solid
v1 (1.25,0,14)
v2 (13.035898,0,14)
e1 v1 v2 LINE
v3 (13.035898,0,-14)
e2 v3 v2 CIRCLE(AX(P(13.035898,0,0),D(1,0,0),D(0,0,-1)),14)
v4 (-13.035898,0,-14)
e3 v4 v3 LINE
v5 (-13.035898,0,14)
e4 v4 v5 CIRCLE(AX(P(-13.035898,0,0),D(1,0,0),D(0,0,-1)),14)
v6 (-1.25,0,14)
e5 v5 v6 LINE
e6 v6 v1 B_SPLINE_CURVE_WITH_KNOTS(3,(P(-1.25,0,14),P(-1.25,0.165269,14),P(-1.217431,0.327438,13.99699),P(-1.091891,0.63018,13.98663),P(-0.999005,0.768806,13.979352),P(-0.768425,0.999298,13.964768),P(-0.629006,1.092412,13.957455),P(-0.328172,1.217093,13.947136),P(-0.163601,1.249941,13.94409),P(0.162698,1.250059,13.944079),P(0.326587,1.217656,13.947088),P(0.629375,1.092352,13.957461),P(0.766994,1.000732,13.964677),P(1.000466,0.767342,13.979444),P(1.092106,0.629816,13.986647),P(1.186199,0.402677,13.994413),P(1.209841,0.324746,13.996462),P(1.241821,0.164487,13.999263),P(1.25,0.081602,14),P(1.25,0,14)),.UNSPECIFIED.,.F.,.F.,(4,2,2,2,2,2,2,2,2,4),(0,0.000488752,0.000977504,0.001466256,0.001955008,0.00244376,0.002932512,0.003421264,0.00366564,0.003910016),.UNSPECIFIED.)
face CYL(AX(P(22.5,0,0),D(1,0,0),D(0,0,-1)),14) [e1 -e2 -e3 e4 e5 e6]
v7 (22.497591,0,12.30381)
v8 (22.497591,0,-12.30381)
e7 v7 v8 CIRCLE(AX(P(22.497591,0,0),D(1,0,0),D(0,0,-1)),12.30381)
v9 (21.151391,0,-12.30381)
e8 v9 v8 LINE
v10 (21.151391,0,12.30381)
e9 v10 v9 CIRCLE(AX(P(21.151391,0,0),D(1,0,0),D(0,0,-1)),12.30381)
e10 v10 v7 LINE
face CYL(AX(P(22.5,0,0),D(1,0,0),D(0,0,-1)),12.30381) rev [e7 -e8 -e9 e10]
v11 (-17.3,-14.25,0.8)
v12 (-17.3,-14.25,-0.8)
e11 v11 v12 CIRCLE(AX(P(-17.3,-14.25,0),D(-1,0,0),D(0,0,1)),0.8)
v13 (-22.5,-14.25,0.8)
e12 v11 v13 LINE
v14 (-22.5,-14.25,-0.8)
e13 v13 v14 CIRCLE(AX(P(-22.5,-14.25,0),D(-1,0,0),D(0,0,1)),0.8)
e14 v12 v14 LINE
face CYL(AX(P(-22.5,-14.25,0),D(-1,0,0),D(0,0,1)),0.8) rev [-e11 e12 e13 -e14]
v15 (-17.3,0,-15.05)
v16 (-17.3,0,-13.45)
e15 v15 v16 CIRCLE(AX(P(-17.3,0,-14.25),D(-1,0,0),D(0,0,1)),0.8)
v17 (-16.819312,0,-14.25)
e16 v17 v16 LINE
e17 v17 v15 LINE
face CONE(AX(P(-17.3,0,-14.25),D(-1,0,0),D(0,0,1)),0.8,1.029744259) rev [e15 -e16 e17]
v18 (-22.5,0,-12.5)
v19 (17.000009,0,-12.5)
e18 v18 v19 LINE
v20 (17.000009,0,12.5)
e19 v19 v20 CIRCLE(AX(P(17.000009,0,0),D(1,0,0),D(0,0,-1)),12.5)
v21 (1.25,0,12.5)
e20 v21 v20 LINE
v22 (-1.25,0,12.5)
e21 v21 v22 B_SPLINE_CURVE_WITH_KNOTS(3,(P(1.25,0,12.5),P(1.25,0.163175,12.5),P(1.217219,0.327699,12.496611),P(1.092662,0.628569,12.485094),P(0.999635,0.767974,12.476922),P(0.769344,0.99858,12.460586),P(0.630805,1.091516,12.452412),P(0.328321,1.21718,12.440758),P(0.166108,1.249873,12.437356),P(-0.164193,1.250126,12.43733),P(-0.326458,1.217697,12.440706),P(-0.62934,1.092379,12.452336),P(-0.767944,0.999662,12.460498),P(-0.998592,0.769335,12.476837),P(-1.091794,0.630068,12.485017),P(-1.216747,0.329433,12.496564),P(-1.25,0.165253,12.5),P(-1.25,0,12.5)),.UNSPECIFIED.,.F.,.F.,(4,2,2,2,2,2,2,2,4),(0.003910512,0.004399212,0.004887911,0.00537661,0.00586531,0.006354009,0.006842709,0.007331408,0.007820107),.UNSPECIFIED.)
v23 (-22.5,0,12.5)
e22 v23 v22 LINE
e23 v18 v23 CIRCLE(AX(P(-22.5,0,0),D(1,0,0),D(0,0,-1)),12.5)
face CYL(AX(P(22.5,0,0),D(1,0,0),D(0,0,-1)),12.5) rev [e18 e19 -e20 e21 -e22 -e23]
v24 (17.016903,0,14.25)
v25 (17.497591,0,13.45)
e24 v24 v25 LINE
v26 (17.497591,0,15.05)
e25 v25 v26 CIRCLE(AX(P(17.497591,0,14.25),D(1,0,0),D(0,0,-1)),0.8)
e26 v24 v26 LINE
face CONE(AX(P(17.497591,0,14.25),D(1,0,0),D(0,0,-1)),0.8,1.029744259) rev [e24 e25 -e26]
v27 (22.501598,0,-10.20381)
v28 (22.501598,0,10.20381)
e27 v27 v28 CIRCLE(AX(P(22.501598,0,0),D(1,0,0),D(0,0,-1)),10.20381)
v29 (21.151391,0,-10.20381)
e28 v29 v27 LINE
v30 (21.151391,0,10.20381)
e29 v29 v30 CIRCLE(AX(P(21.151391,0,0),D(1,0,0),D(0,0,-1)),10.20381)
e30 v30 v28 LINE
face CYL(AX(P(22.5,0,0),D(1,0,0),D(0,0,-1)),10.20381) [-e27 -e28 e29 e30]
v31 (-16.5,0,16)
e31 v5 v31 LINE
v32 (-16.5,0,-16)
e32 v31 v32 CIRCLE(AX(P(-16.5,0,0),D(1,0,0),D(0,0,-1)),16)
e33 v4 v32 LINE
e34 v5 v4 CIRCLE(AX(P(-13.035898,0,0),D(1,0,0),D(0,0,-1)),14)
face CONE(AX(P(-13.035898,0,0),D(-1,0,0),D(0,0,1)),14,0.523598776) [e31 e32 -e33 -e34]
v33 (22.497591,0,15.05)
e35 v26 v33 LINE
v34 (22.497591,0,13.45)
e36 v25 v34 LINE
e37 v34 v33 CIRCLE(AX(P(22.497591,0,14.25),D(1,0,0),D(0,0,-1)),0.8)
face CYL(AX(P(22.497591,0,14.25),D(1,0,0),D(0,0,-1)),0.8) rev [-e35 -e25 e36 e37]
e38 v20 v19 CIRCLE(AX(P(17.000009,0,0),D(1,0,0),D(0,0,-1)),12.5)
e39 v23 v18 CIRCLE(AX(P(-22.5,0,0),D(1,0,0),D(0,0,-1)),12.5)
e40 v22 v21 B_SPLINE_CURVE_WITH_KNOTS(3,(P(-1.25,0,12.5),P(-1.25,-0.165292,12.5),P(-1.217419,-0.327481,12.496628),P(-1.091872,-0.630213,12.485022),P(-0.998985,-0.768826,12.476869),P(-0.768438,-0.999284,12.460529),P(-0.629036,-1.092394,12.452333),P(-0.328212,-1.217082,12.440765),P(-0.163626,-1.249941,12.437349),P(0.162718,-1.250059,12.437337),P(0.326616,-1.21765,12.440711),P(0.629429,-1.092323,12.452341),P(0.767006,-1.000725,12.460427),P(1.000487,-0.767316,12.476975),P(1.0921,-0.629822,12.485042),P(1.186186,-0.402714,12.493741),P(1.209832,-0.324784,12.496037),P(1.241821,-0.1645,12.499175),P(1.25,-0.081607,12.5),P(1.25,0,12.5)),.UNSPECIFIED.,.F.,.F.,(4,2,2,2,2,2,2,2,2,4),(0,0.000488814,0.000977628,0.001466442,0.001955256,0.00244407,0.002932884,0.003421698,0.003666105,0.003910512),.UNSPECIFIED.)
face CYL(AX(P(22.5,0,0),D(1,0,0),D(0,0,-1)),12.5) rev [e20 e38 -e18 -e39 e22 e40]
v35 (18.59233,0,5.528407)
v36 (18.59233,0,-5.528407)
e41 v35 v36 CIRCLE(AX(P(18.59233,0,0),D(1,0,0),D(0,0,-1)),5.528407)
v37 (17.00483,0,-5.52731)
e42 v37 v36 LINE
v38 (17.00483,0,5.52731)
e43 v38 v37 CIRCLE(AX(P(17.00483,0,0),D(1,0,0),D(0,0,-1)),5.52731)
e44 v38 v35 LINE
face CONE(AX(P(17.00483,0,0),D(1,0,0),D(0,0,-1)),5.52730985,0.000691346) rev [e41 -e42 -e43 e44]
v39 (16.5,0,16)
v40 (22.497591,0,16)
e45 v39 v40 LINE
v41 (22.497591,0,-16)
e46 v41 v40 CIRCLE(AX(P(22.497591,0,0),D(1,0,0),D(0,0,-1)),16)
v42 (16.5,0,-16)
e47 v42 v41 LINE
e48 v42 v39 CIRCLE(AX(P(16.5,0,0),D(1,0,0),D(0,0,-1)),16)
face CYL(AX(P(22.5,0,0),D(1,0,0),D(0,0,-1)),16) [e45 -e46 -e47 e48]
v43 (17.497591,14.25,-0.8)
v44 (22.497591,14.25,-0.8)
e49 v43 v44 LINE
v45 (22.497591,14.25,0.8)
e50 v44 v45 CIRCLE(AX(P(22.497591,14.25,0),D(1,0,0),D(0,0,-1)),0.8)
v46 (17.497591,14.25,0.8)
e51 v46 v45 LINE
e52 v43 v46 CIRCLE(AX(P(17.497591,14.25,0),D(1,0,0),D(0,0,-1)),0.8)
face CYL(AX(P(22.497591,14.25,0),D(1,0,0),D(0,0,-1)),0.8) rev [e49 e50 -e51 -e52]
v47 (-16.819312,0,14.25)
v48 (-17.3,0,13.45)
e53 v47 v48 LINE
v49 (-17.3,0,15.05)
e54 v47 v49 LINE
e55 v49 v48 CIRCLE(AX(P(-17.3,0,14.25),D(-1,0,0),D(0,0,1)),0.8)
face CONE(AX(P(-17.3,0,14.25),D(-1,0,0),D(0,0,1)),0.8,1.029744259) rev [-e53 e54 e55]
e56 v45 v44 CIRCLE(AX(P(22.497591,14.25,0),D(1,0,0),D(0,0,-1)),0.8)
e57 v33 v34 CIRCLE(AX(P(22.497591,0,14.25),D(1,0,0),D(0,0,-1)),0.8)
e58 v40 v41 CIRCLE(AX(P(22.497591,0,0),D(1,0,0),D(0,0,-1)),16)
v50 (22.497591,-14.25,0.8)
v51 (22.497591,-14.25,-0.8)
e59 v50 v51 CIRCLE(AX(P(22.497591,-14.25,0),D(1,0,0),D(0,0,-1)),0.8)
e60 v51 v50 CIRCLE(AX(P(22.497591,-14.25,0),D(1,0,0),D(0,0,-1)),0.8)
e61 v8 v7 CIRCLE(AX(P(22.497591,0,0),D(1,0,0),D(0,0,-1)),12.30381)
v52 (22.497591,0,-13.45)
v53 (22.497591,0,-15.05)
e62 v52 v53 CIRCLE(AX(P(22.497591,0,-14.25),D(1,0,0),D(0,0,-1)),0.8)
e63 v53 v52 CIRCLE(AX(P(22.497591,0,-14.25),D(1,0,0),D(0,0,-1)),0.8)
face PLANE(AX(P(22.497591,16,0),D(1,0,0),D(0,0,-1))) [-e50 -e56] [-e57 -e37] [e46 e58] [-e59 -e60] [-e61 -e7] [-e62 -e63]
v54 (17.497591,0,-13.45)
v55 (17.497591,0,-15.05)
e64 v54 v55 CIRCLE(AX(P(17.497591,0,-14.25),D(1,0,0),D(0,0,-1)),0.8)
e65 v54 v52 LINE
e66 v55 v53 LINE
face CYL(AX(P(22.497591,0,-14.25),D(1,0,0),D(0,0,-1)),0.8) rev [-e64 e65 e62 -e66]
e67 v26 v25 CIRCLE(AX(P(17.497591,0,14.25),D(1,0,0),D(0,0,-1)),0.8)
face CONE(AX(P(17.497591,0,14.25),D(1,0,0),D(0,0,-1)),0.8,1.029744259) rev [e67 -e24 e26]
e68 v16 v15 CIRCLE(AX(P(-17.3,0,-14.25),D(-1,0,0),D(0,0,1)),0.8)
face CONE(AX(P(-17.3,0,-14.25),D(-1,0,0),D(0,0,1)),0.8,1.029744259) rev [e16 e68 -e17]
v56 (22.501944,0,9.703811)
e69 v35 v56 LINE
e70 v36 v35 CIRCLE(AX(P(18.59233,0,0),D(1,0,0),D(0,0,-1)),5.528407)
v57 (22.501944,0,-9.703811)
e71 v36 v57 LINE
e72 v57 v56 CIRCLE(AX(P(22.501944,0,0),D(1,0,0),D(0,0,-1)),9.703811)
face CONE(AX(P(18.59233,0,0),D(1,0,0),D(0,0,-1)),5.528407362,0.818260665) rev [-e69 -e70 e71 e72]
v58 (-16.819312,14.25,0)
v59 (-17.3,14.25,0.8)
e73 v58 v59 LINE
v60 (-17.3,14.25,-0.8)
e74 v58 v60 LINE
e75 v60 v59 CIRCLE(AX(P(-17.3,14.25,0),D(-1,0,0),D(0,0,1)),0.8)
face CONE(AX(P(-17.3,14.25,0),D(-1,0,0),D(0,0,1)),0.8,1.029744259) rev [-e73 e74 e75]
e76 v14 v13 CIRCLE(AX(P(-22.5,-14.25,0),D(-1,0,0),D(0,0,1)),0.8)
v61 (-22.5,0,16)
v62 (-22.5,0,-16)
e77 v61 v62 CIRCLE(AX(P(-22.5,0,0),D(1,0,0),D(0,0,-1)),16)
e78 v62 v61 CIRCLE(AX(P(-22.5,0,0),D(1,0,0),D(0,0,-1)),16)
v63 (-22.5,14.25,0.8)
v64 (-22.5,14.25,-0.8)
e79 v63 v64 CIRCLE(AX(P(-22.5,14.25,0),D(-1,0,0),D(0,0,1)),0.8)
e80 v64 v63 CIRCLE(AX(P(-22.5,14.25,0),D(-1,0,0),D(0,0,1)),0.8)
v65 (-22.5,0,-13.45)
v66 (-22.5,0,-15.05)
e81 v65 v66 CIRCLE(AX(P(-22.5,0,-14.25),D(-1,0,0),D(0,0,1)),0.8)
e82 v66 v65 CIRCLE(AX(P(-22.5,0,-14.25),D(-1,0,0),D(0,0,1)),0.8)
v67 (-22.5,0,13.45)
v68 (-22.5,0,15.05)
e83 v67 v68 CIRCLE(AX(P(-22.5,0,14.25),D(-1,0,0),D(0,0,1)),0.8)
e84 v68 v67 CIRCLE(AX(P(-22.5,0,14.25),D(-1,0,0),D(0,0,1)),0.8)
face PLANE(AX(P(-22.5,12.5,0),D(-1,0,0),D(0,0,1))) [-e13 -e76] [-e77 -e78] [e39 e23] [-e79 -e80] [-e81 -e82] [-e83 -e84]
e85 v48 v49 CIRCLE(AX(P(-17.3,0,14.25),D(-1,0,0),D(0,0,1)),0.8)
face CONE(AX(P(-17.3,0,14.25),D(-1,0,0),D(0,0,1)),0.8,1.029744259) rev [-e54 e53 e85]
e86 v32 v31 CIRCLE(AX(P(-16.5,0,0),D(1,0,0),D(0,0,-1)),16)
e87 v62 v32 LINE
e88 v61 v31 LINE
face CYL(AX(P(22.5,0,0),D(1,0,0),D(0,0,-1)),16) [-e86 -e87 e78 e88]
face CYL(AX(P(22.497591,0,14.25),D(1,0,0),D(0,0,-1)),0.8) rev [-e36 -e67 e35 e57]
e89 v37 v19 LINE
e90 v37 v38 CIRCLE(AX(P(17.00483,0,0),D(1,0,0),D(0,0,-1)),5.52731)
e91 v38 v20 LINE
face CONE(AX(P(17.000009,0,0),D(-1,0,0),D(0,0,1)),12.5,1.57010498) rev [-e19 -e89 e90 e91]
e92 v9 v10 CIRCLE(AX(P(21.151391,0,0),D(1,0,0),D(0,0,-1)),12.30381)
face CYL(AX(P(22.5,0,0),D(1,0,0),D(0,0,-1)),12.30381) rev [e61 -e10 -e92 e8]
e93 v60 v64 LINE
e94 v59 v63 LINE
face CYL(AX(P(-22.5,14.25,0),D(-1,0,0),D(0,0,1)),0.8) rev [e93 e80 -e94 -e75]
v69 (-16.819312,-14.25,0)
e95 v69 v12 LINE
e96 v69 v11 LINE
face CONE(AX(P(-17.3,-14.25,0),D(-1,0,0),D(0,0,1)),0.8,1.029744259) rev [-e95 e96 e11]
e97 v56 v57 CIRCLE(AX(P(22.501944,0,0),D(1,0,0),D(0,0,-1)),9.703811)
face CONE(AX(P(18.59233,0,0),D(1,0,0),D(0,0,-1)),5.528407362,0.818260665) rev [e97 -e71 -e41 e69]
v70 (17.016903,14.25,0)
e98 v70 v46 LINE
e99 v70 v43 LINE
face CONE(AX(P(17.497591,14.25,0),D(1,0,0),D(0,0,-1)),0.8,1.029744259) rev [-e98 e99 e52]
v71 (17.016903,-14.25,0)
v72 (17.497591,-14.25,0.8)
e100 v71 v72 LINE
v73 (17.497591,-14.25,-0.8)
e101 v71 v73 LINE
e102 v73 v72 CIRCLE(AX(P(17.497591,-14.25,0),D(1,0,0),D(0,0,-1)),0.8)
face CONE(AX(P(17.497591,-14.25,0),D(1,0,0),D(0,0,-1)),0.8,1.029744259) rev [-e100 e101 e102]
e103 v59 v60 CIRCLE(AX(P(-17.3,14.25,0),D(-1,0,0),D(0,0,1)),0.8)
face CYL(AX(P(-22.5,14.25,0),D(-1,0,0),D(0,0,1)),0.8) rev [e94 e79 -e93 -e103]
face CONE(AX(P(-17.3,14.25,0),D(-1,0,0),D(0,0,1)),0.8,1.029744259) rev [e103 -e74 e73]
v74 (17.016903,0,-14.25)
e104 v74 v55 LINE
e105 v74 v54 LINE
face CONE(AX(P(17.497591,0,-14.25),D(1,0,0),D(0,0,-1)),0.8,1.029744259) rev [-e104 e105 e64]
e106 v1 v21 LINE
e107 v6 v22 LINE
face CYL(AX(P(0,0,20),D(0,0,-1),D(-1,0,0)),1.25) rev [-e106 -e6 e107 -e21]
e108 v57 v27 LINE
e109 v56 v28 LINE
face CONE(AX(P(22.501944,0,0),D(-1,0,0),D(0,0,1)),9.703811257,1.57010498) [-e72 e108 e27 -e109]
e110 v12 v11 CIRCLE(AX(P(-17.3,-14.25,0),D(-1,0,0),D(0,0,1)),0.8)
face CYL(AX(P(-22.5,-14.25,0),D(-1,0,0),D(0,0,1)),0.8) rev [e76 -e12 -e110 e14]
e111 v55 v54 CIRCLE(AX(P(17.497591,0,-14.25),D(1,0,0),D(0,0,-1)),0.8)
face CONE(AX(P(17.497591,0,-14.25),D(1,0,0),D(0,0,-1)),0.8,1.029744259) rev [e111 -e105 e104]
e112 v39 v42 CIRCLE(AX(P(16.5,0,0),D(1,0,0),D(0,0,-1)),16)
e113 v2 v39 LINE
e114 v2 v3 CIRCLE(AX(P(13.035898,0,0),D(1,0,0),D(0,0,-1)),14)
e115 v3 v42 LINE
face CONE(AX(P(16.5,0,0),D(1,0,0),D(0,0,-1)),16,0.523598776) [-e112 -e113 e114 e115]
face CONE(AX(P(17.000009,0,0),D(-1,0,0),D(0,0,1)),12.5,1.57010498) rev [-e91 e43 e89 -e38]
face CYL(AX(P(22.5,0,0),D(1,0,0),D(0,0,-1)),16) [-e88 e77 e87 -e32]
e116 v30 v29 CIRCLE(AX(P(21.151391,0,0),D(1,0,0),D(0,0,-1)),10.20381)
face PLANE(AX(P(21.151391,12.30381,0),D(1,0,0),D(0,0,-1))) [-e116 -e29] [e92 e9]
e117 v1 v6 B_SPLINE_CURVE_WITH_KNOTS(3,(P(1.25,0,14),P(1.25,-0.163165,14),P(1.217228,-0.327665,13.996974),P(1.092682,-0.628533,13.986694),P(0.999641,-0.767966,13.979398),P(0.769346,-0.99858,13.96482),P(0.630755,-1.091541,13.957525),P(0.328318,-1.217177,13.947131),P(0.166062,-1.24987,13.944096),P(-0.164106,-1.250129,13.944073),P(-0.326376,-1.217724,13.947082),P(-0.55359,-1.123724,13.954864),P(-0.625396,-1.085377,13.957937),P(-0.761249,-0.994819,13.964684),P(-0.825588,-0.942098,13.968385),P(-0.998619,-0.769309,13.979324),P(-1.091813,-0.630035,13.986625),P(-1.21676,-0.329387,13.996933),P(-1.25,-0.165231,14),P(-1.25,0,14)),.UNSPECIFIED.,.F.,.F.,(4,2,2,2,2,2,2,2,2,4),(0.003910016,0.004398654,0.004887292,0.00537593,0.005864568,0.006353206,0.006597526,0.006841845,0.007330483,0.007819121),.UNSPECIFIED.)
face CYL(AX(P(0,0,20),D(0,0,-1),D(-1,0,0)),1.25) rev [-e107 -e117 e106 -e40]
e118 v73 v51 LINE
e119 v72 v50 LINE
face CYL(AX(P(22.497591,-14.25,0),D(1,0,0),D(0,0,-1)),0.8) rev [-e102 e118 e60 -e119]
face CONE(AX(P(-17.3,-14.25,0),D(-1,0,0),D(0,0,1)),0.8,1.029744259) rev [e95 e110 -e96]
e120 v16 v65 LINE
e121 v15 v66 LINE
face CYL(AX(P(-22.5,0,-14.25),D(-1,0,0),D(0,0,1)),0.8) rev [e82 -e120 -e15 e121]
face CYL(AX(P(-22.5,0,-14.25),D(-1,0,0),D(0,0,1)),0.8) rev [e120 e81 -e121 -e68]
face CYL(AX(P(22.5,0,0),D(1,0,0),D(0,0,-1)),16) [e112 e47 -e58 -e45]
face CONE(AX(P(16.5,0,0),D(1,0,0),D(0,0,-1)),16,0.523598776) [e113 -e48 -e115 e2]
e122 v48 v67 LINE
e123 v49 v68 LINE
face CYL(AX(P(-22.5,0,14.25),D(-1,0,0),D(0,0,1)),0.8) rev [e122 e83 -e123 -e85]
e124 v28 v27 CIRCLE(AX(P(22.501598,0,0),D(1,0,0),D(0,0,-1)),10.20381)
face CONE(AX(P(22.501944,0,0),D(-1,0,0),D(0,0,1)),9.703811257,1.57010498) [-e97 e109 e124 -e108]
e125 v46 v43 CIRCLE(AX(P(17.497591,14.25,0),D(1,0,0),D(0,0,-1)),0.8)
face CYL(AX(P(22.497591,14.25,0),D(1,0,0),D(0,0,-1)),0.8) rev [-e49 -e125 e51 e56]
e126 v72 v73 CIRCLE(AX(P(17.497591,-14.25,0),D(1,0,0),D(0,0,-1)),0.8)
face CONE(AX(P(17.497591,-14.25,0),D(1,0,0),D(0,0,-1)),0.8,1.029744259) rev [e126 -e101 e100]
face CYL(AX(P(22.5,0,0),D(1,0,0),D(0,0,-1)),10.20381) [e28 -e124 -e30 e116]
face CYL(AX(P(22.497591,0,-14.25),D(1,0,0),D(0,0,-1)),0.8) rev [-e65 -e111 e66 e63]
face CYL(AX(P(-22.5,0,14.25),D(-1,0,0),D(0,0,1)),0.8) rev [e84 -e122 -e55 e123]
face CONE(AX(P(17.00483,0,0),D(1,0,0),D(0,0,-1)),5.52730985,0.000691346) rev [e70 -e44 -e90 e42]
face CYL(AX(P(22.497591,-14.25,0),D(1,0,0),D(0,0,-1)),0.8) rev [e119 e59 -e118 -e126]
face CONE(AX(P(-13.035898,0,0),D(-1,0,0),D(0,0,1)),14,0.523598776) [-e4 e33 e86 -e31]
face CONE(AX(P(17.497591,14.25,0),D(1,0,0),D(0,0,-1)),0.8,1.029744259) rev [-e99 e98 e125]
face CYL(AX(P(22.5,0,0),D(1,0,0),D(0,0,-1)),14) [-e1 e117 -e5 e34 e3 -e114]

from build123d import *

# Parameters (mm, degrees)
HOLE_WIZARD_M2_1_D     = 1.6
HOLE_WIZARD_M2_1_DEPTH = 5
HOLE_WIZARD_M2_1_TIP   = 0.480688495
HOLE_WIZARD_M2_2_D     = 1.6
HOLE_WIZARD_M2_2_DEPTH = 5.2
HOLE_WIZARD_M2_2_TIP   = 0.480688495
SKETCH_9_R             = 1.25
CUT_EXTRUDE_1_DEPTH    = 20


with BuildPart() as part:
    # 草图1 → 旋转1 (revolve)
    with BuildSketch(Plane.XY, mode=Mode.PRIVATE) as revolve_1_sk:
        Polygon((16.5, 16), (13.035898385, 14), (-13.035898385, 14), (-16.5, 16), (-22.5, 16), (-22.5, 12.5), (17.00000944, 12.5), (17.004829984, 5.52730985), (18.592329605, 5.528407362), (22.501943889, 9.703811257), (22.501598217, 10.203809753), (21.151391042, 10.203809753), (21.151391042, 12.303809753), (22.497591042, 12.303809753), (22.497591042, 16), align=None)
    revolve(revolve_1_sk.sketch.rotate(Axis((22.5, 0, 0), (-1, 0, 0)), 90), axis=Axis((22.5, 0, 0), (-1, 0, 0)))

    # M2 螺纹孔1
    with Locations(Plane(origin=(22.497591042, 0, 0), x_dir=(0, 0, -1), z_dir=(1, 0, 0))):
        with Locations((0, 14.25), (14.25, 0), (0, -14.25), (-14.25, 0), (0, 0)):
            Hole(HOLE_WIZARD_M2_1_D / 2, depth=HOLE_WIZARD_M2_1_DEPTH)
            with Locations((0, 0, -(HOLE_WIZARD_M2_1_DEPTH + HOLE_WIZARD_M2_1_TIP / 2))):  # 118° drill point
                Cone(0, HOLE_WIZARD_M2_1_D / 2, HOLE_WIZARD_M2_1_TIP, mode=Mode.SUBTRACT)

    # M2 螺纹孔2
    with Locations(Plane.ZY.offset(22.5)):
        with Locations((0, 14.25), (14.25, 0), (0, -14.25), (-14.25, 0), (0, 0)):
            Hole(HOLE_WIZARD_M2_2_D / 2, depth=HOLE_WIZARD_M2_2_DEPTH)
            with Locations((0, 0, -(HOLE_WIZARD_M2_2_DEPTH + HOLE_WIZARD_M2_2_TIP / 2))):  # 118° drill point
                Cone(0, HOLE_WIZARD_M2_2_D / 2, HOLE_WIZARD_M2_2_TIP, mode=Mode.SUBTRACT)

    # 草图9 → 切除-拉伸1 (cut)
    with BuildSketch(Plane.XY):
        with Locations(Location((0, 0, 0), (0, 0, 180))):
            Circle(SKETCH_9_R)
    extrude(amount=CUT_EXTRUDE_1_DEPTH, mode=Mode.SUBTRACT)


solid = part.part
